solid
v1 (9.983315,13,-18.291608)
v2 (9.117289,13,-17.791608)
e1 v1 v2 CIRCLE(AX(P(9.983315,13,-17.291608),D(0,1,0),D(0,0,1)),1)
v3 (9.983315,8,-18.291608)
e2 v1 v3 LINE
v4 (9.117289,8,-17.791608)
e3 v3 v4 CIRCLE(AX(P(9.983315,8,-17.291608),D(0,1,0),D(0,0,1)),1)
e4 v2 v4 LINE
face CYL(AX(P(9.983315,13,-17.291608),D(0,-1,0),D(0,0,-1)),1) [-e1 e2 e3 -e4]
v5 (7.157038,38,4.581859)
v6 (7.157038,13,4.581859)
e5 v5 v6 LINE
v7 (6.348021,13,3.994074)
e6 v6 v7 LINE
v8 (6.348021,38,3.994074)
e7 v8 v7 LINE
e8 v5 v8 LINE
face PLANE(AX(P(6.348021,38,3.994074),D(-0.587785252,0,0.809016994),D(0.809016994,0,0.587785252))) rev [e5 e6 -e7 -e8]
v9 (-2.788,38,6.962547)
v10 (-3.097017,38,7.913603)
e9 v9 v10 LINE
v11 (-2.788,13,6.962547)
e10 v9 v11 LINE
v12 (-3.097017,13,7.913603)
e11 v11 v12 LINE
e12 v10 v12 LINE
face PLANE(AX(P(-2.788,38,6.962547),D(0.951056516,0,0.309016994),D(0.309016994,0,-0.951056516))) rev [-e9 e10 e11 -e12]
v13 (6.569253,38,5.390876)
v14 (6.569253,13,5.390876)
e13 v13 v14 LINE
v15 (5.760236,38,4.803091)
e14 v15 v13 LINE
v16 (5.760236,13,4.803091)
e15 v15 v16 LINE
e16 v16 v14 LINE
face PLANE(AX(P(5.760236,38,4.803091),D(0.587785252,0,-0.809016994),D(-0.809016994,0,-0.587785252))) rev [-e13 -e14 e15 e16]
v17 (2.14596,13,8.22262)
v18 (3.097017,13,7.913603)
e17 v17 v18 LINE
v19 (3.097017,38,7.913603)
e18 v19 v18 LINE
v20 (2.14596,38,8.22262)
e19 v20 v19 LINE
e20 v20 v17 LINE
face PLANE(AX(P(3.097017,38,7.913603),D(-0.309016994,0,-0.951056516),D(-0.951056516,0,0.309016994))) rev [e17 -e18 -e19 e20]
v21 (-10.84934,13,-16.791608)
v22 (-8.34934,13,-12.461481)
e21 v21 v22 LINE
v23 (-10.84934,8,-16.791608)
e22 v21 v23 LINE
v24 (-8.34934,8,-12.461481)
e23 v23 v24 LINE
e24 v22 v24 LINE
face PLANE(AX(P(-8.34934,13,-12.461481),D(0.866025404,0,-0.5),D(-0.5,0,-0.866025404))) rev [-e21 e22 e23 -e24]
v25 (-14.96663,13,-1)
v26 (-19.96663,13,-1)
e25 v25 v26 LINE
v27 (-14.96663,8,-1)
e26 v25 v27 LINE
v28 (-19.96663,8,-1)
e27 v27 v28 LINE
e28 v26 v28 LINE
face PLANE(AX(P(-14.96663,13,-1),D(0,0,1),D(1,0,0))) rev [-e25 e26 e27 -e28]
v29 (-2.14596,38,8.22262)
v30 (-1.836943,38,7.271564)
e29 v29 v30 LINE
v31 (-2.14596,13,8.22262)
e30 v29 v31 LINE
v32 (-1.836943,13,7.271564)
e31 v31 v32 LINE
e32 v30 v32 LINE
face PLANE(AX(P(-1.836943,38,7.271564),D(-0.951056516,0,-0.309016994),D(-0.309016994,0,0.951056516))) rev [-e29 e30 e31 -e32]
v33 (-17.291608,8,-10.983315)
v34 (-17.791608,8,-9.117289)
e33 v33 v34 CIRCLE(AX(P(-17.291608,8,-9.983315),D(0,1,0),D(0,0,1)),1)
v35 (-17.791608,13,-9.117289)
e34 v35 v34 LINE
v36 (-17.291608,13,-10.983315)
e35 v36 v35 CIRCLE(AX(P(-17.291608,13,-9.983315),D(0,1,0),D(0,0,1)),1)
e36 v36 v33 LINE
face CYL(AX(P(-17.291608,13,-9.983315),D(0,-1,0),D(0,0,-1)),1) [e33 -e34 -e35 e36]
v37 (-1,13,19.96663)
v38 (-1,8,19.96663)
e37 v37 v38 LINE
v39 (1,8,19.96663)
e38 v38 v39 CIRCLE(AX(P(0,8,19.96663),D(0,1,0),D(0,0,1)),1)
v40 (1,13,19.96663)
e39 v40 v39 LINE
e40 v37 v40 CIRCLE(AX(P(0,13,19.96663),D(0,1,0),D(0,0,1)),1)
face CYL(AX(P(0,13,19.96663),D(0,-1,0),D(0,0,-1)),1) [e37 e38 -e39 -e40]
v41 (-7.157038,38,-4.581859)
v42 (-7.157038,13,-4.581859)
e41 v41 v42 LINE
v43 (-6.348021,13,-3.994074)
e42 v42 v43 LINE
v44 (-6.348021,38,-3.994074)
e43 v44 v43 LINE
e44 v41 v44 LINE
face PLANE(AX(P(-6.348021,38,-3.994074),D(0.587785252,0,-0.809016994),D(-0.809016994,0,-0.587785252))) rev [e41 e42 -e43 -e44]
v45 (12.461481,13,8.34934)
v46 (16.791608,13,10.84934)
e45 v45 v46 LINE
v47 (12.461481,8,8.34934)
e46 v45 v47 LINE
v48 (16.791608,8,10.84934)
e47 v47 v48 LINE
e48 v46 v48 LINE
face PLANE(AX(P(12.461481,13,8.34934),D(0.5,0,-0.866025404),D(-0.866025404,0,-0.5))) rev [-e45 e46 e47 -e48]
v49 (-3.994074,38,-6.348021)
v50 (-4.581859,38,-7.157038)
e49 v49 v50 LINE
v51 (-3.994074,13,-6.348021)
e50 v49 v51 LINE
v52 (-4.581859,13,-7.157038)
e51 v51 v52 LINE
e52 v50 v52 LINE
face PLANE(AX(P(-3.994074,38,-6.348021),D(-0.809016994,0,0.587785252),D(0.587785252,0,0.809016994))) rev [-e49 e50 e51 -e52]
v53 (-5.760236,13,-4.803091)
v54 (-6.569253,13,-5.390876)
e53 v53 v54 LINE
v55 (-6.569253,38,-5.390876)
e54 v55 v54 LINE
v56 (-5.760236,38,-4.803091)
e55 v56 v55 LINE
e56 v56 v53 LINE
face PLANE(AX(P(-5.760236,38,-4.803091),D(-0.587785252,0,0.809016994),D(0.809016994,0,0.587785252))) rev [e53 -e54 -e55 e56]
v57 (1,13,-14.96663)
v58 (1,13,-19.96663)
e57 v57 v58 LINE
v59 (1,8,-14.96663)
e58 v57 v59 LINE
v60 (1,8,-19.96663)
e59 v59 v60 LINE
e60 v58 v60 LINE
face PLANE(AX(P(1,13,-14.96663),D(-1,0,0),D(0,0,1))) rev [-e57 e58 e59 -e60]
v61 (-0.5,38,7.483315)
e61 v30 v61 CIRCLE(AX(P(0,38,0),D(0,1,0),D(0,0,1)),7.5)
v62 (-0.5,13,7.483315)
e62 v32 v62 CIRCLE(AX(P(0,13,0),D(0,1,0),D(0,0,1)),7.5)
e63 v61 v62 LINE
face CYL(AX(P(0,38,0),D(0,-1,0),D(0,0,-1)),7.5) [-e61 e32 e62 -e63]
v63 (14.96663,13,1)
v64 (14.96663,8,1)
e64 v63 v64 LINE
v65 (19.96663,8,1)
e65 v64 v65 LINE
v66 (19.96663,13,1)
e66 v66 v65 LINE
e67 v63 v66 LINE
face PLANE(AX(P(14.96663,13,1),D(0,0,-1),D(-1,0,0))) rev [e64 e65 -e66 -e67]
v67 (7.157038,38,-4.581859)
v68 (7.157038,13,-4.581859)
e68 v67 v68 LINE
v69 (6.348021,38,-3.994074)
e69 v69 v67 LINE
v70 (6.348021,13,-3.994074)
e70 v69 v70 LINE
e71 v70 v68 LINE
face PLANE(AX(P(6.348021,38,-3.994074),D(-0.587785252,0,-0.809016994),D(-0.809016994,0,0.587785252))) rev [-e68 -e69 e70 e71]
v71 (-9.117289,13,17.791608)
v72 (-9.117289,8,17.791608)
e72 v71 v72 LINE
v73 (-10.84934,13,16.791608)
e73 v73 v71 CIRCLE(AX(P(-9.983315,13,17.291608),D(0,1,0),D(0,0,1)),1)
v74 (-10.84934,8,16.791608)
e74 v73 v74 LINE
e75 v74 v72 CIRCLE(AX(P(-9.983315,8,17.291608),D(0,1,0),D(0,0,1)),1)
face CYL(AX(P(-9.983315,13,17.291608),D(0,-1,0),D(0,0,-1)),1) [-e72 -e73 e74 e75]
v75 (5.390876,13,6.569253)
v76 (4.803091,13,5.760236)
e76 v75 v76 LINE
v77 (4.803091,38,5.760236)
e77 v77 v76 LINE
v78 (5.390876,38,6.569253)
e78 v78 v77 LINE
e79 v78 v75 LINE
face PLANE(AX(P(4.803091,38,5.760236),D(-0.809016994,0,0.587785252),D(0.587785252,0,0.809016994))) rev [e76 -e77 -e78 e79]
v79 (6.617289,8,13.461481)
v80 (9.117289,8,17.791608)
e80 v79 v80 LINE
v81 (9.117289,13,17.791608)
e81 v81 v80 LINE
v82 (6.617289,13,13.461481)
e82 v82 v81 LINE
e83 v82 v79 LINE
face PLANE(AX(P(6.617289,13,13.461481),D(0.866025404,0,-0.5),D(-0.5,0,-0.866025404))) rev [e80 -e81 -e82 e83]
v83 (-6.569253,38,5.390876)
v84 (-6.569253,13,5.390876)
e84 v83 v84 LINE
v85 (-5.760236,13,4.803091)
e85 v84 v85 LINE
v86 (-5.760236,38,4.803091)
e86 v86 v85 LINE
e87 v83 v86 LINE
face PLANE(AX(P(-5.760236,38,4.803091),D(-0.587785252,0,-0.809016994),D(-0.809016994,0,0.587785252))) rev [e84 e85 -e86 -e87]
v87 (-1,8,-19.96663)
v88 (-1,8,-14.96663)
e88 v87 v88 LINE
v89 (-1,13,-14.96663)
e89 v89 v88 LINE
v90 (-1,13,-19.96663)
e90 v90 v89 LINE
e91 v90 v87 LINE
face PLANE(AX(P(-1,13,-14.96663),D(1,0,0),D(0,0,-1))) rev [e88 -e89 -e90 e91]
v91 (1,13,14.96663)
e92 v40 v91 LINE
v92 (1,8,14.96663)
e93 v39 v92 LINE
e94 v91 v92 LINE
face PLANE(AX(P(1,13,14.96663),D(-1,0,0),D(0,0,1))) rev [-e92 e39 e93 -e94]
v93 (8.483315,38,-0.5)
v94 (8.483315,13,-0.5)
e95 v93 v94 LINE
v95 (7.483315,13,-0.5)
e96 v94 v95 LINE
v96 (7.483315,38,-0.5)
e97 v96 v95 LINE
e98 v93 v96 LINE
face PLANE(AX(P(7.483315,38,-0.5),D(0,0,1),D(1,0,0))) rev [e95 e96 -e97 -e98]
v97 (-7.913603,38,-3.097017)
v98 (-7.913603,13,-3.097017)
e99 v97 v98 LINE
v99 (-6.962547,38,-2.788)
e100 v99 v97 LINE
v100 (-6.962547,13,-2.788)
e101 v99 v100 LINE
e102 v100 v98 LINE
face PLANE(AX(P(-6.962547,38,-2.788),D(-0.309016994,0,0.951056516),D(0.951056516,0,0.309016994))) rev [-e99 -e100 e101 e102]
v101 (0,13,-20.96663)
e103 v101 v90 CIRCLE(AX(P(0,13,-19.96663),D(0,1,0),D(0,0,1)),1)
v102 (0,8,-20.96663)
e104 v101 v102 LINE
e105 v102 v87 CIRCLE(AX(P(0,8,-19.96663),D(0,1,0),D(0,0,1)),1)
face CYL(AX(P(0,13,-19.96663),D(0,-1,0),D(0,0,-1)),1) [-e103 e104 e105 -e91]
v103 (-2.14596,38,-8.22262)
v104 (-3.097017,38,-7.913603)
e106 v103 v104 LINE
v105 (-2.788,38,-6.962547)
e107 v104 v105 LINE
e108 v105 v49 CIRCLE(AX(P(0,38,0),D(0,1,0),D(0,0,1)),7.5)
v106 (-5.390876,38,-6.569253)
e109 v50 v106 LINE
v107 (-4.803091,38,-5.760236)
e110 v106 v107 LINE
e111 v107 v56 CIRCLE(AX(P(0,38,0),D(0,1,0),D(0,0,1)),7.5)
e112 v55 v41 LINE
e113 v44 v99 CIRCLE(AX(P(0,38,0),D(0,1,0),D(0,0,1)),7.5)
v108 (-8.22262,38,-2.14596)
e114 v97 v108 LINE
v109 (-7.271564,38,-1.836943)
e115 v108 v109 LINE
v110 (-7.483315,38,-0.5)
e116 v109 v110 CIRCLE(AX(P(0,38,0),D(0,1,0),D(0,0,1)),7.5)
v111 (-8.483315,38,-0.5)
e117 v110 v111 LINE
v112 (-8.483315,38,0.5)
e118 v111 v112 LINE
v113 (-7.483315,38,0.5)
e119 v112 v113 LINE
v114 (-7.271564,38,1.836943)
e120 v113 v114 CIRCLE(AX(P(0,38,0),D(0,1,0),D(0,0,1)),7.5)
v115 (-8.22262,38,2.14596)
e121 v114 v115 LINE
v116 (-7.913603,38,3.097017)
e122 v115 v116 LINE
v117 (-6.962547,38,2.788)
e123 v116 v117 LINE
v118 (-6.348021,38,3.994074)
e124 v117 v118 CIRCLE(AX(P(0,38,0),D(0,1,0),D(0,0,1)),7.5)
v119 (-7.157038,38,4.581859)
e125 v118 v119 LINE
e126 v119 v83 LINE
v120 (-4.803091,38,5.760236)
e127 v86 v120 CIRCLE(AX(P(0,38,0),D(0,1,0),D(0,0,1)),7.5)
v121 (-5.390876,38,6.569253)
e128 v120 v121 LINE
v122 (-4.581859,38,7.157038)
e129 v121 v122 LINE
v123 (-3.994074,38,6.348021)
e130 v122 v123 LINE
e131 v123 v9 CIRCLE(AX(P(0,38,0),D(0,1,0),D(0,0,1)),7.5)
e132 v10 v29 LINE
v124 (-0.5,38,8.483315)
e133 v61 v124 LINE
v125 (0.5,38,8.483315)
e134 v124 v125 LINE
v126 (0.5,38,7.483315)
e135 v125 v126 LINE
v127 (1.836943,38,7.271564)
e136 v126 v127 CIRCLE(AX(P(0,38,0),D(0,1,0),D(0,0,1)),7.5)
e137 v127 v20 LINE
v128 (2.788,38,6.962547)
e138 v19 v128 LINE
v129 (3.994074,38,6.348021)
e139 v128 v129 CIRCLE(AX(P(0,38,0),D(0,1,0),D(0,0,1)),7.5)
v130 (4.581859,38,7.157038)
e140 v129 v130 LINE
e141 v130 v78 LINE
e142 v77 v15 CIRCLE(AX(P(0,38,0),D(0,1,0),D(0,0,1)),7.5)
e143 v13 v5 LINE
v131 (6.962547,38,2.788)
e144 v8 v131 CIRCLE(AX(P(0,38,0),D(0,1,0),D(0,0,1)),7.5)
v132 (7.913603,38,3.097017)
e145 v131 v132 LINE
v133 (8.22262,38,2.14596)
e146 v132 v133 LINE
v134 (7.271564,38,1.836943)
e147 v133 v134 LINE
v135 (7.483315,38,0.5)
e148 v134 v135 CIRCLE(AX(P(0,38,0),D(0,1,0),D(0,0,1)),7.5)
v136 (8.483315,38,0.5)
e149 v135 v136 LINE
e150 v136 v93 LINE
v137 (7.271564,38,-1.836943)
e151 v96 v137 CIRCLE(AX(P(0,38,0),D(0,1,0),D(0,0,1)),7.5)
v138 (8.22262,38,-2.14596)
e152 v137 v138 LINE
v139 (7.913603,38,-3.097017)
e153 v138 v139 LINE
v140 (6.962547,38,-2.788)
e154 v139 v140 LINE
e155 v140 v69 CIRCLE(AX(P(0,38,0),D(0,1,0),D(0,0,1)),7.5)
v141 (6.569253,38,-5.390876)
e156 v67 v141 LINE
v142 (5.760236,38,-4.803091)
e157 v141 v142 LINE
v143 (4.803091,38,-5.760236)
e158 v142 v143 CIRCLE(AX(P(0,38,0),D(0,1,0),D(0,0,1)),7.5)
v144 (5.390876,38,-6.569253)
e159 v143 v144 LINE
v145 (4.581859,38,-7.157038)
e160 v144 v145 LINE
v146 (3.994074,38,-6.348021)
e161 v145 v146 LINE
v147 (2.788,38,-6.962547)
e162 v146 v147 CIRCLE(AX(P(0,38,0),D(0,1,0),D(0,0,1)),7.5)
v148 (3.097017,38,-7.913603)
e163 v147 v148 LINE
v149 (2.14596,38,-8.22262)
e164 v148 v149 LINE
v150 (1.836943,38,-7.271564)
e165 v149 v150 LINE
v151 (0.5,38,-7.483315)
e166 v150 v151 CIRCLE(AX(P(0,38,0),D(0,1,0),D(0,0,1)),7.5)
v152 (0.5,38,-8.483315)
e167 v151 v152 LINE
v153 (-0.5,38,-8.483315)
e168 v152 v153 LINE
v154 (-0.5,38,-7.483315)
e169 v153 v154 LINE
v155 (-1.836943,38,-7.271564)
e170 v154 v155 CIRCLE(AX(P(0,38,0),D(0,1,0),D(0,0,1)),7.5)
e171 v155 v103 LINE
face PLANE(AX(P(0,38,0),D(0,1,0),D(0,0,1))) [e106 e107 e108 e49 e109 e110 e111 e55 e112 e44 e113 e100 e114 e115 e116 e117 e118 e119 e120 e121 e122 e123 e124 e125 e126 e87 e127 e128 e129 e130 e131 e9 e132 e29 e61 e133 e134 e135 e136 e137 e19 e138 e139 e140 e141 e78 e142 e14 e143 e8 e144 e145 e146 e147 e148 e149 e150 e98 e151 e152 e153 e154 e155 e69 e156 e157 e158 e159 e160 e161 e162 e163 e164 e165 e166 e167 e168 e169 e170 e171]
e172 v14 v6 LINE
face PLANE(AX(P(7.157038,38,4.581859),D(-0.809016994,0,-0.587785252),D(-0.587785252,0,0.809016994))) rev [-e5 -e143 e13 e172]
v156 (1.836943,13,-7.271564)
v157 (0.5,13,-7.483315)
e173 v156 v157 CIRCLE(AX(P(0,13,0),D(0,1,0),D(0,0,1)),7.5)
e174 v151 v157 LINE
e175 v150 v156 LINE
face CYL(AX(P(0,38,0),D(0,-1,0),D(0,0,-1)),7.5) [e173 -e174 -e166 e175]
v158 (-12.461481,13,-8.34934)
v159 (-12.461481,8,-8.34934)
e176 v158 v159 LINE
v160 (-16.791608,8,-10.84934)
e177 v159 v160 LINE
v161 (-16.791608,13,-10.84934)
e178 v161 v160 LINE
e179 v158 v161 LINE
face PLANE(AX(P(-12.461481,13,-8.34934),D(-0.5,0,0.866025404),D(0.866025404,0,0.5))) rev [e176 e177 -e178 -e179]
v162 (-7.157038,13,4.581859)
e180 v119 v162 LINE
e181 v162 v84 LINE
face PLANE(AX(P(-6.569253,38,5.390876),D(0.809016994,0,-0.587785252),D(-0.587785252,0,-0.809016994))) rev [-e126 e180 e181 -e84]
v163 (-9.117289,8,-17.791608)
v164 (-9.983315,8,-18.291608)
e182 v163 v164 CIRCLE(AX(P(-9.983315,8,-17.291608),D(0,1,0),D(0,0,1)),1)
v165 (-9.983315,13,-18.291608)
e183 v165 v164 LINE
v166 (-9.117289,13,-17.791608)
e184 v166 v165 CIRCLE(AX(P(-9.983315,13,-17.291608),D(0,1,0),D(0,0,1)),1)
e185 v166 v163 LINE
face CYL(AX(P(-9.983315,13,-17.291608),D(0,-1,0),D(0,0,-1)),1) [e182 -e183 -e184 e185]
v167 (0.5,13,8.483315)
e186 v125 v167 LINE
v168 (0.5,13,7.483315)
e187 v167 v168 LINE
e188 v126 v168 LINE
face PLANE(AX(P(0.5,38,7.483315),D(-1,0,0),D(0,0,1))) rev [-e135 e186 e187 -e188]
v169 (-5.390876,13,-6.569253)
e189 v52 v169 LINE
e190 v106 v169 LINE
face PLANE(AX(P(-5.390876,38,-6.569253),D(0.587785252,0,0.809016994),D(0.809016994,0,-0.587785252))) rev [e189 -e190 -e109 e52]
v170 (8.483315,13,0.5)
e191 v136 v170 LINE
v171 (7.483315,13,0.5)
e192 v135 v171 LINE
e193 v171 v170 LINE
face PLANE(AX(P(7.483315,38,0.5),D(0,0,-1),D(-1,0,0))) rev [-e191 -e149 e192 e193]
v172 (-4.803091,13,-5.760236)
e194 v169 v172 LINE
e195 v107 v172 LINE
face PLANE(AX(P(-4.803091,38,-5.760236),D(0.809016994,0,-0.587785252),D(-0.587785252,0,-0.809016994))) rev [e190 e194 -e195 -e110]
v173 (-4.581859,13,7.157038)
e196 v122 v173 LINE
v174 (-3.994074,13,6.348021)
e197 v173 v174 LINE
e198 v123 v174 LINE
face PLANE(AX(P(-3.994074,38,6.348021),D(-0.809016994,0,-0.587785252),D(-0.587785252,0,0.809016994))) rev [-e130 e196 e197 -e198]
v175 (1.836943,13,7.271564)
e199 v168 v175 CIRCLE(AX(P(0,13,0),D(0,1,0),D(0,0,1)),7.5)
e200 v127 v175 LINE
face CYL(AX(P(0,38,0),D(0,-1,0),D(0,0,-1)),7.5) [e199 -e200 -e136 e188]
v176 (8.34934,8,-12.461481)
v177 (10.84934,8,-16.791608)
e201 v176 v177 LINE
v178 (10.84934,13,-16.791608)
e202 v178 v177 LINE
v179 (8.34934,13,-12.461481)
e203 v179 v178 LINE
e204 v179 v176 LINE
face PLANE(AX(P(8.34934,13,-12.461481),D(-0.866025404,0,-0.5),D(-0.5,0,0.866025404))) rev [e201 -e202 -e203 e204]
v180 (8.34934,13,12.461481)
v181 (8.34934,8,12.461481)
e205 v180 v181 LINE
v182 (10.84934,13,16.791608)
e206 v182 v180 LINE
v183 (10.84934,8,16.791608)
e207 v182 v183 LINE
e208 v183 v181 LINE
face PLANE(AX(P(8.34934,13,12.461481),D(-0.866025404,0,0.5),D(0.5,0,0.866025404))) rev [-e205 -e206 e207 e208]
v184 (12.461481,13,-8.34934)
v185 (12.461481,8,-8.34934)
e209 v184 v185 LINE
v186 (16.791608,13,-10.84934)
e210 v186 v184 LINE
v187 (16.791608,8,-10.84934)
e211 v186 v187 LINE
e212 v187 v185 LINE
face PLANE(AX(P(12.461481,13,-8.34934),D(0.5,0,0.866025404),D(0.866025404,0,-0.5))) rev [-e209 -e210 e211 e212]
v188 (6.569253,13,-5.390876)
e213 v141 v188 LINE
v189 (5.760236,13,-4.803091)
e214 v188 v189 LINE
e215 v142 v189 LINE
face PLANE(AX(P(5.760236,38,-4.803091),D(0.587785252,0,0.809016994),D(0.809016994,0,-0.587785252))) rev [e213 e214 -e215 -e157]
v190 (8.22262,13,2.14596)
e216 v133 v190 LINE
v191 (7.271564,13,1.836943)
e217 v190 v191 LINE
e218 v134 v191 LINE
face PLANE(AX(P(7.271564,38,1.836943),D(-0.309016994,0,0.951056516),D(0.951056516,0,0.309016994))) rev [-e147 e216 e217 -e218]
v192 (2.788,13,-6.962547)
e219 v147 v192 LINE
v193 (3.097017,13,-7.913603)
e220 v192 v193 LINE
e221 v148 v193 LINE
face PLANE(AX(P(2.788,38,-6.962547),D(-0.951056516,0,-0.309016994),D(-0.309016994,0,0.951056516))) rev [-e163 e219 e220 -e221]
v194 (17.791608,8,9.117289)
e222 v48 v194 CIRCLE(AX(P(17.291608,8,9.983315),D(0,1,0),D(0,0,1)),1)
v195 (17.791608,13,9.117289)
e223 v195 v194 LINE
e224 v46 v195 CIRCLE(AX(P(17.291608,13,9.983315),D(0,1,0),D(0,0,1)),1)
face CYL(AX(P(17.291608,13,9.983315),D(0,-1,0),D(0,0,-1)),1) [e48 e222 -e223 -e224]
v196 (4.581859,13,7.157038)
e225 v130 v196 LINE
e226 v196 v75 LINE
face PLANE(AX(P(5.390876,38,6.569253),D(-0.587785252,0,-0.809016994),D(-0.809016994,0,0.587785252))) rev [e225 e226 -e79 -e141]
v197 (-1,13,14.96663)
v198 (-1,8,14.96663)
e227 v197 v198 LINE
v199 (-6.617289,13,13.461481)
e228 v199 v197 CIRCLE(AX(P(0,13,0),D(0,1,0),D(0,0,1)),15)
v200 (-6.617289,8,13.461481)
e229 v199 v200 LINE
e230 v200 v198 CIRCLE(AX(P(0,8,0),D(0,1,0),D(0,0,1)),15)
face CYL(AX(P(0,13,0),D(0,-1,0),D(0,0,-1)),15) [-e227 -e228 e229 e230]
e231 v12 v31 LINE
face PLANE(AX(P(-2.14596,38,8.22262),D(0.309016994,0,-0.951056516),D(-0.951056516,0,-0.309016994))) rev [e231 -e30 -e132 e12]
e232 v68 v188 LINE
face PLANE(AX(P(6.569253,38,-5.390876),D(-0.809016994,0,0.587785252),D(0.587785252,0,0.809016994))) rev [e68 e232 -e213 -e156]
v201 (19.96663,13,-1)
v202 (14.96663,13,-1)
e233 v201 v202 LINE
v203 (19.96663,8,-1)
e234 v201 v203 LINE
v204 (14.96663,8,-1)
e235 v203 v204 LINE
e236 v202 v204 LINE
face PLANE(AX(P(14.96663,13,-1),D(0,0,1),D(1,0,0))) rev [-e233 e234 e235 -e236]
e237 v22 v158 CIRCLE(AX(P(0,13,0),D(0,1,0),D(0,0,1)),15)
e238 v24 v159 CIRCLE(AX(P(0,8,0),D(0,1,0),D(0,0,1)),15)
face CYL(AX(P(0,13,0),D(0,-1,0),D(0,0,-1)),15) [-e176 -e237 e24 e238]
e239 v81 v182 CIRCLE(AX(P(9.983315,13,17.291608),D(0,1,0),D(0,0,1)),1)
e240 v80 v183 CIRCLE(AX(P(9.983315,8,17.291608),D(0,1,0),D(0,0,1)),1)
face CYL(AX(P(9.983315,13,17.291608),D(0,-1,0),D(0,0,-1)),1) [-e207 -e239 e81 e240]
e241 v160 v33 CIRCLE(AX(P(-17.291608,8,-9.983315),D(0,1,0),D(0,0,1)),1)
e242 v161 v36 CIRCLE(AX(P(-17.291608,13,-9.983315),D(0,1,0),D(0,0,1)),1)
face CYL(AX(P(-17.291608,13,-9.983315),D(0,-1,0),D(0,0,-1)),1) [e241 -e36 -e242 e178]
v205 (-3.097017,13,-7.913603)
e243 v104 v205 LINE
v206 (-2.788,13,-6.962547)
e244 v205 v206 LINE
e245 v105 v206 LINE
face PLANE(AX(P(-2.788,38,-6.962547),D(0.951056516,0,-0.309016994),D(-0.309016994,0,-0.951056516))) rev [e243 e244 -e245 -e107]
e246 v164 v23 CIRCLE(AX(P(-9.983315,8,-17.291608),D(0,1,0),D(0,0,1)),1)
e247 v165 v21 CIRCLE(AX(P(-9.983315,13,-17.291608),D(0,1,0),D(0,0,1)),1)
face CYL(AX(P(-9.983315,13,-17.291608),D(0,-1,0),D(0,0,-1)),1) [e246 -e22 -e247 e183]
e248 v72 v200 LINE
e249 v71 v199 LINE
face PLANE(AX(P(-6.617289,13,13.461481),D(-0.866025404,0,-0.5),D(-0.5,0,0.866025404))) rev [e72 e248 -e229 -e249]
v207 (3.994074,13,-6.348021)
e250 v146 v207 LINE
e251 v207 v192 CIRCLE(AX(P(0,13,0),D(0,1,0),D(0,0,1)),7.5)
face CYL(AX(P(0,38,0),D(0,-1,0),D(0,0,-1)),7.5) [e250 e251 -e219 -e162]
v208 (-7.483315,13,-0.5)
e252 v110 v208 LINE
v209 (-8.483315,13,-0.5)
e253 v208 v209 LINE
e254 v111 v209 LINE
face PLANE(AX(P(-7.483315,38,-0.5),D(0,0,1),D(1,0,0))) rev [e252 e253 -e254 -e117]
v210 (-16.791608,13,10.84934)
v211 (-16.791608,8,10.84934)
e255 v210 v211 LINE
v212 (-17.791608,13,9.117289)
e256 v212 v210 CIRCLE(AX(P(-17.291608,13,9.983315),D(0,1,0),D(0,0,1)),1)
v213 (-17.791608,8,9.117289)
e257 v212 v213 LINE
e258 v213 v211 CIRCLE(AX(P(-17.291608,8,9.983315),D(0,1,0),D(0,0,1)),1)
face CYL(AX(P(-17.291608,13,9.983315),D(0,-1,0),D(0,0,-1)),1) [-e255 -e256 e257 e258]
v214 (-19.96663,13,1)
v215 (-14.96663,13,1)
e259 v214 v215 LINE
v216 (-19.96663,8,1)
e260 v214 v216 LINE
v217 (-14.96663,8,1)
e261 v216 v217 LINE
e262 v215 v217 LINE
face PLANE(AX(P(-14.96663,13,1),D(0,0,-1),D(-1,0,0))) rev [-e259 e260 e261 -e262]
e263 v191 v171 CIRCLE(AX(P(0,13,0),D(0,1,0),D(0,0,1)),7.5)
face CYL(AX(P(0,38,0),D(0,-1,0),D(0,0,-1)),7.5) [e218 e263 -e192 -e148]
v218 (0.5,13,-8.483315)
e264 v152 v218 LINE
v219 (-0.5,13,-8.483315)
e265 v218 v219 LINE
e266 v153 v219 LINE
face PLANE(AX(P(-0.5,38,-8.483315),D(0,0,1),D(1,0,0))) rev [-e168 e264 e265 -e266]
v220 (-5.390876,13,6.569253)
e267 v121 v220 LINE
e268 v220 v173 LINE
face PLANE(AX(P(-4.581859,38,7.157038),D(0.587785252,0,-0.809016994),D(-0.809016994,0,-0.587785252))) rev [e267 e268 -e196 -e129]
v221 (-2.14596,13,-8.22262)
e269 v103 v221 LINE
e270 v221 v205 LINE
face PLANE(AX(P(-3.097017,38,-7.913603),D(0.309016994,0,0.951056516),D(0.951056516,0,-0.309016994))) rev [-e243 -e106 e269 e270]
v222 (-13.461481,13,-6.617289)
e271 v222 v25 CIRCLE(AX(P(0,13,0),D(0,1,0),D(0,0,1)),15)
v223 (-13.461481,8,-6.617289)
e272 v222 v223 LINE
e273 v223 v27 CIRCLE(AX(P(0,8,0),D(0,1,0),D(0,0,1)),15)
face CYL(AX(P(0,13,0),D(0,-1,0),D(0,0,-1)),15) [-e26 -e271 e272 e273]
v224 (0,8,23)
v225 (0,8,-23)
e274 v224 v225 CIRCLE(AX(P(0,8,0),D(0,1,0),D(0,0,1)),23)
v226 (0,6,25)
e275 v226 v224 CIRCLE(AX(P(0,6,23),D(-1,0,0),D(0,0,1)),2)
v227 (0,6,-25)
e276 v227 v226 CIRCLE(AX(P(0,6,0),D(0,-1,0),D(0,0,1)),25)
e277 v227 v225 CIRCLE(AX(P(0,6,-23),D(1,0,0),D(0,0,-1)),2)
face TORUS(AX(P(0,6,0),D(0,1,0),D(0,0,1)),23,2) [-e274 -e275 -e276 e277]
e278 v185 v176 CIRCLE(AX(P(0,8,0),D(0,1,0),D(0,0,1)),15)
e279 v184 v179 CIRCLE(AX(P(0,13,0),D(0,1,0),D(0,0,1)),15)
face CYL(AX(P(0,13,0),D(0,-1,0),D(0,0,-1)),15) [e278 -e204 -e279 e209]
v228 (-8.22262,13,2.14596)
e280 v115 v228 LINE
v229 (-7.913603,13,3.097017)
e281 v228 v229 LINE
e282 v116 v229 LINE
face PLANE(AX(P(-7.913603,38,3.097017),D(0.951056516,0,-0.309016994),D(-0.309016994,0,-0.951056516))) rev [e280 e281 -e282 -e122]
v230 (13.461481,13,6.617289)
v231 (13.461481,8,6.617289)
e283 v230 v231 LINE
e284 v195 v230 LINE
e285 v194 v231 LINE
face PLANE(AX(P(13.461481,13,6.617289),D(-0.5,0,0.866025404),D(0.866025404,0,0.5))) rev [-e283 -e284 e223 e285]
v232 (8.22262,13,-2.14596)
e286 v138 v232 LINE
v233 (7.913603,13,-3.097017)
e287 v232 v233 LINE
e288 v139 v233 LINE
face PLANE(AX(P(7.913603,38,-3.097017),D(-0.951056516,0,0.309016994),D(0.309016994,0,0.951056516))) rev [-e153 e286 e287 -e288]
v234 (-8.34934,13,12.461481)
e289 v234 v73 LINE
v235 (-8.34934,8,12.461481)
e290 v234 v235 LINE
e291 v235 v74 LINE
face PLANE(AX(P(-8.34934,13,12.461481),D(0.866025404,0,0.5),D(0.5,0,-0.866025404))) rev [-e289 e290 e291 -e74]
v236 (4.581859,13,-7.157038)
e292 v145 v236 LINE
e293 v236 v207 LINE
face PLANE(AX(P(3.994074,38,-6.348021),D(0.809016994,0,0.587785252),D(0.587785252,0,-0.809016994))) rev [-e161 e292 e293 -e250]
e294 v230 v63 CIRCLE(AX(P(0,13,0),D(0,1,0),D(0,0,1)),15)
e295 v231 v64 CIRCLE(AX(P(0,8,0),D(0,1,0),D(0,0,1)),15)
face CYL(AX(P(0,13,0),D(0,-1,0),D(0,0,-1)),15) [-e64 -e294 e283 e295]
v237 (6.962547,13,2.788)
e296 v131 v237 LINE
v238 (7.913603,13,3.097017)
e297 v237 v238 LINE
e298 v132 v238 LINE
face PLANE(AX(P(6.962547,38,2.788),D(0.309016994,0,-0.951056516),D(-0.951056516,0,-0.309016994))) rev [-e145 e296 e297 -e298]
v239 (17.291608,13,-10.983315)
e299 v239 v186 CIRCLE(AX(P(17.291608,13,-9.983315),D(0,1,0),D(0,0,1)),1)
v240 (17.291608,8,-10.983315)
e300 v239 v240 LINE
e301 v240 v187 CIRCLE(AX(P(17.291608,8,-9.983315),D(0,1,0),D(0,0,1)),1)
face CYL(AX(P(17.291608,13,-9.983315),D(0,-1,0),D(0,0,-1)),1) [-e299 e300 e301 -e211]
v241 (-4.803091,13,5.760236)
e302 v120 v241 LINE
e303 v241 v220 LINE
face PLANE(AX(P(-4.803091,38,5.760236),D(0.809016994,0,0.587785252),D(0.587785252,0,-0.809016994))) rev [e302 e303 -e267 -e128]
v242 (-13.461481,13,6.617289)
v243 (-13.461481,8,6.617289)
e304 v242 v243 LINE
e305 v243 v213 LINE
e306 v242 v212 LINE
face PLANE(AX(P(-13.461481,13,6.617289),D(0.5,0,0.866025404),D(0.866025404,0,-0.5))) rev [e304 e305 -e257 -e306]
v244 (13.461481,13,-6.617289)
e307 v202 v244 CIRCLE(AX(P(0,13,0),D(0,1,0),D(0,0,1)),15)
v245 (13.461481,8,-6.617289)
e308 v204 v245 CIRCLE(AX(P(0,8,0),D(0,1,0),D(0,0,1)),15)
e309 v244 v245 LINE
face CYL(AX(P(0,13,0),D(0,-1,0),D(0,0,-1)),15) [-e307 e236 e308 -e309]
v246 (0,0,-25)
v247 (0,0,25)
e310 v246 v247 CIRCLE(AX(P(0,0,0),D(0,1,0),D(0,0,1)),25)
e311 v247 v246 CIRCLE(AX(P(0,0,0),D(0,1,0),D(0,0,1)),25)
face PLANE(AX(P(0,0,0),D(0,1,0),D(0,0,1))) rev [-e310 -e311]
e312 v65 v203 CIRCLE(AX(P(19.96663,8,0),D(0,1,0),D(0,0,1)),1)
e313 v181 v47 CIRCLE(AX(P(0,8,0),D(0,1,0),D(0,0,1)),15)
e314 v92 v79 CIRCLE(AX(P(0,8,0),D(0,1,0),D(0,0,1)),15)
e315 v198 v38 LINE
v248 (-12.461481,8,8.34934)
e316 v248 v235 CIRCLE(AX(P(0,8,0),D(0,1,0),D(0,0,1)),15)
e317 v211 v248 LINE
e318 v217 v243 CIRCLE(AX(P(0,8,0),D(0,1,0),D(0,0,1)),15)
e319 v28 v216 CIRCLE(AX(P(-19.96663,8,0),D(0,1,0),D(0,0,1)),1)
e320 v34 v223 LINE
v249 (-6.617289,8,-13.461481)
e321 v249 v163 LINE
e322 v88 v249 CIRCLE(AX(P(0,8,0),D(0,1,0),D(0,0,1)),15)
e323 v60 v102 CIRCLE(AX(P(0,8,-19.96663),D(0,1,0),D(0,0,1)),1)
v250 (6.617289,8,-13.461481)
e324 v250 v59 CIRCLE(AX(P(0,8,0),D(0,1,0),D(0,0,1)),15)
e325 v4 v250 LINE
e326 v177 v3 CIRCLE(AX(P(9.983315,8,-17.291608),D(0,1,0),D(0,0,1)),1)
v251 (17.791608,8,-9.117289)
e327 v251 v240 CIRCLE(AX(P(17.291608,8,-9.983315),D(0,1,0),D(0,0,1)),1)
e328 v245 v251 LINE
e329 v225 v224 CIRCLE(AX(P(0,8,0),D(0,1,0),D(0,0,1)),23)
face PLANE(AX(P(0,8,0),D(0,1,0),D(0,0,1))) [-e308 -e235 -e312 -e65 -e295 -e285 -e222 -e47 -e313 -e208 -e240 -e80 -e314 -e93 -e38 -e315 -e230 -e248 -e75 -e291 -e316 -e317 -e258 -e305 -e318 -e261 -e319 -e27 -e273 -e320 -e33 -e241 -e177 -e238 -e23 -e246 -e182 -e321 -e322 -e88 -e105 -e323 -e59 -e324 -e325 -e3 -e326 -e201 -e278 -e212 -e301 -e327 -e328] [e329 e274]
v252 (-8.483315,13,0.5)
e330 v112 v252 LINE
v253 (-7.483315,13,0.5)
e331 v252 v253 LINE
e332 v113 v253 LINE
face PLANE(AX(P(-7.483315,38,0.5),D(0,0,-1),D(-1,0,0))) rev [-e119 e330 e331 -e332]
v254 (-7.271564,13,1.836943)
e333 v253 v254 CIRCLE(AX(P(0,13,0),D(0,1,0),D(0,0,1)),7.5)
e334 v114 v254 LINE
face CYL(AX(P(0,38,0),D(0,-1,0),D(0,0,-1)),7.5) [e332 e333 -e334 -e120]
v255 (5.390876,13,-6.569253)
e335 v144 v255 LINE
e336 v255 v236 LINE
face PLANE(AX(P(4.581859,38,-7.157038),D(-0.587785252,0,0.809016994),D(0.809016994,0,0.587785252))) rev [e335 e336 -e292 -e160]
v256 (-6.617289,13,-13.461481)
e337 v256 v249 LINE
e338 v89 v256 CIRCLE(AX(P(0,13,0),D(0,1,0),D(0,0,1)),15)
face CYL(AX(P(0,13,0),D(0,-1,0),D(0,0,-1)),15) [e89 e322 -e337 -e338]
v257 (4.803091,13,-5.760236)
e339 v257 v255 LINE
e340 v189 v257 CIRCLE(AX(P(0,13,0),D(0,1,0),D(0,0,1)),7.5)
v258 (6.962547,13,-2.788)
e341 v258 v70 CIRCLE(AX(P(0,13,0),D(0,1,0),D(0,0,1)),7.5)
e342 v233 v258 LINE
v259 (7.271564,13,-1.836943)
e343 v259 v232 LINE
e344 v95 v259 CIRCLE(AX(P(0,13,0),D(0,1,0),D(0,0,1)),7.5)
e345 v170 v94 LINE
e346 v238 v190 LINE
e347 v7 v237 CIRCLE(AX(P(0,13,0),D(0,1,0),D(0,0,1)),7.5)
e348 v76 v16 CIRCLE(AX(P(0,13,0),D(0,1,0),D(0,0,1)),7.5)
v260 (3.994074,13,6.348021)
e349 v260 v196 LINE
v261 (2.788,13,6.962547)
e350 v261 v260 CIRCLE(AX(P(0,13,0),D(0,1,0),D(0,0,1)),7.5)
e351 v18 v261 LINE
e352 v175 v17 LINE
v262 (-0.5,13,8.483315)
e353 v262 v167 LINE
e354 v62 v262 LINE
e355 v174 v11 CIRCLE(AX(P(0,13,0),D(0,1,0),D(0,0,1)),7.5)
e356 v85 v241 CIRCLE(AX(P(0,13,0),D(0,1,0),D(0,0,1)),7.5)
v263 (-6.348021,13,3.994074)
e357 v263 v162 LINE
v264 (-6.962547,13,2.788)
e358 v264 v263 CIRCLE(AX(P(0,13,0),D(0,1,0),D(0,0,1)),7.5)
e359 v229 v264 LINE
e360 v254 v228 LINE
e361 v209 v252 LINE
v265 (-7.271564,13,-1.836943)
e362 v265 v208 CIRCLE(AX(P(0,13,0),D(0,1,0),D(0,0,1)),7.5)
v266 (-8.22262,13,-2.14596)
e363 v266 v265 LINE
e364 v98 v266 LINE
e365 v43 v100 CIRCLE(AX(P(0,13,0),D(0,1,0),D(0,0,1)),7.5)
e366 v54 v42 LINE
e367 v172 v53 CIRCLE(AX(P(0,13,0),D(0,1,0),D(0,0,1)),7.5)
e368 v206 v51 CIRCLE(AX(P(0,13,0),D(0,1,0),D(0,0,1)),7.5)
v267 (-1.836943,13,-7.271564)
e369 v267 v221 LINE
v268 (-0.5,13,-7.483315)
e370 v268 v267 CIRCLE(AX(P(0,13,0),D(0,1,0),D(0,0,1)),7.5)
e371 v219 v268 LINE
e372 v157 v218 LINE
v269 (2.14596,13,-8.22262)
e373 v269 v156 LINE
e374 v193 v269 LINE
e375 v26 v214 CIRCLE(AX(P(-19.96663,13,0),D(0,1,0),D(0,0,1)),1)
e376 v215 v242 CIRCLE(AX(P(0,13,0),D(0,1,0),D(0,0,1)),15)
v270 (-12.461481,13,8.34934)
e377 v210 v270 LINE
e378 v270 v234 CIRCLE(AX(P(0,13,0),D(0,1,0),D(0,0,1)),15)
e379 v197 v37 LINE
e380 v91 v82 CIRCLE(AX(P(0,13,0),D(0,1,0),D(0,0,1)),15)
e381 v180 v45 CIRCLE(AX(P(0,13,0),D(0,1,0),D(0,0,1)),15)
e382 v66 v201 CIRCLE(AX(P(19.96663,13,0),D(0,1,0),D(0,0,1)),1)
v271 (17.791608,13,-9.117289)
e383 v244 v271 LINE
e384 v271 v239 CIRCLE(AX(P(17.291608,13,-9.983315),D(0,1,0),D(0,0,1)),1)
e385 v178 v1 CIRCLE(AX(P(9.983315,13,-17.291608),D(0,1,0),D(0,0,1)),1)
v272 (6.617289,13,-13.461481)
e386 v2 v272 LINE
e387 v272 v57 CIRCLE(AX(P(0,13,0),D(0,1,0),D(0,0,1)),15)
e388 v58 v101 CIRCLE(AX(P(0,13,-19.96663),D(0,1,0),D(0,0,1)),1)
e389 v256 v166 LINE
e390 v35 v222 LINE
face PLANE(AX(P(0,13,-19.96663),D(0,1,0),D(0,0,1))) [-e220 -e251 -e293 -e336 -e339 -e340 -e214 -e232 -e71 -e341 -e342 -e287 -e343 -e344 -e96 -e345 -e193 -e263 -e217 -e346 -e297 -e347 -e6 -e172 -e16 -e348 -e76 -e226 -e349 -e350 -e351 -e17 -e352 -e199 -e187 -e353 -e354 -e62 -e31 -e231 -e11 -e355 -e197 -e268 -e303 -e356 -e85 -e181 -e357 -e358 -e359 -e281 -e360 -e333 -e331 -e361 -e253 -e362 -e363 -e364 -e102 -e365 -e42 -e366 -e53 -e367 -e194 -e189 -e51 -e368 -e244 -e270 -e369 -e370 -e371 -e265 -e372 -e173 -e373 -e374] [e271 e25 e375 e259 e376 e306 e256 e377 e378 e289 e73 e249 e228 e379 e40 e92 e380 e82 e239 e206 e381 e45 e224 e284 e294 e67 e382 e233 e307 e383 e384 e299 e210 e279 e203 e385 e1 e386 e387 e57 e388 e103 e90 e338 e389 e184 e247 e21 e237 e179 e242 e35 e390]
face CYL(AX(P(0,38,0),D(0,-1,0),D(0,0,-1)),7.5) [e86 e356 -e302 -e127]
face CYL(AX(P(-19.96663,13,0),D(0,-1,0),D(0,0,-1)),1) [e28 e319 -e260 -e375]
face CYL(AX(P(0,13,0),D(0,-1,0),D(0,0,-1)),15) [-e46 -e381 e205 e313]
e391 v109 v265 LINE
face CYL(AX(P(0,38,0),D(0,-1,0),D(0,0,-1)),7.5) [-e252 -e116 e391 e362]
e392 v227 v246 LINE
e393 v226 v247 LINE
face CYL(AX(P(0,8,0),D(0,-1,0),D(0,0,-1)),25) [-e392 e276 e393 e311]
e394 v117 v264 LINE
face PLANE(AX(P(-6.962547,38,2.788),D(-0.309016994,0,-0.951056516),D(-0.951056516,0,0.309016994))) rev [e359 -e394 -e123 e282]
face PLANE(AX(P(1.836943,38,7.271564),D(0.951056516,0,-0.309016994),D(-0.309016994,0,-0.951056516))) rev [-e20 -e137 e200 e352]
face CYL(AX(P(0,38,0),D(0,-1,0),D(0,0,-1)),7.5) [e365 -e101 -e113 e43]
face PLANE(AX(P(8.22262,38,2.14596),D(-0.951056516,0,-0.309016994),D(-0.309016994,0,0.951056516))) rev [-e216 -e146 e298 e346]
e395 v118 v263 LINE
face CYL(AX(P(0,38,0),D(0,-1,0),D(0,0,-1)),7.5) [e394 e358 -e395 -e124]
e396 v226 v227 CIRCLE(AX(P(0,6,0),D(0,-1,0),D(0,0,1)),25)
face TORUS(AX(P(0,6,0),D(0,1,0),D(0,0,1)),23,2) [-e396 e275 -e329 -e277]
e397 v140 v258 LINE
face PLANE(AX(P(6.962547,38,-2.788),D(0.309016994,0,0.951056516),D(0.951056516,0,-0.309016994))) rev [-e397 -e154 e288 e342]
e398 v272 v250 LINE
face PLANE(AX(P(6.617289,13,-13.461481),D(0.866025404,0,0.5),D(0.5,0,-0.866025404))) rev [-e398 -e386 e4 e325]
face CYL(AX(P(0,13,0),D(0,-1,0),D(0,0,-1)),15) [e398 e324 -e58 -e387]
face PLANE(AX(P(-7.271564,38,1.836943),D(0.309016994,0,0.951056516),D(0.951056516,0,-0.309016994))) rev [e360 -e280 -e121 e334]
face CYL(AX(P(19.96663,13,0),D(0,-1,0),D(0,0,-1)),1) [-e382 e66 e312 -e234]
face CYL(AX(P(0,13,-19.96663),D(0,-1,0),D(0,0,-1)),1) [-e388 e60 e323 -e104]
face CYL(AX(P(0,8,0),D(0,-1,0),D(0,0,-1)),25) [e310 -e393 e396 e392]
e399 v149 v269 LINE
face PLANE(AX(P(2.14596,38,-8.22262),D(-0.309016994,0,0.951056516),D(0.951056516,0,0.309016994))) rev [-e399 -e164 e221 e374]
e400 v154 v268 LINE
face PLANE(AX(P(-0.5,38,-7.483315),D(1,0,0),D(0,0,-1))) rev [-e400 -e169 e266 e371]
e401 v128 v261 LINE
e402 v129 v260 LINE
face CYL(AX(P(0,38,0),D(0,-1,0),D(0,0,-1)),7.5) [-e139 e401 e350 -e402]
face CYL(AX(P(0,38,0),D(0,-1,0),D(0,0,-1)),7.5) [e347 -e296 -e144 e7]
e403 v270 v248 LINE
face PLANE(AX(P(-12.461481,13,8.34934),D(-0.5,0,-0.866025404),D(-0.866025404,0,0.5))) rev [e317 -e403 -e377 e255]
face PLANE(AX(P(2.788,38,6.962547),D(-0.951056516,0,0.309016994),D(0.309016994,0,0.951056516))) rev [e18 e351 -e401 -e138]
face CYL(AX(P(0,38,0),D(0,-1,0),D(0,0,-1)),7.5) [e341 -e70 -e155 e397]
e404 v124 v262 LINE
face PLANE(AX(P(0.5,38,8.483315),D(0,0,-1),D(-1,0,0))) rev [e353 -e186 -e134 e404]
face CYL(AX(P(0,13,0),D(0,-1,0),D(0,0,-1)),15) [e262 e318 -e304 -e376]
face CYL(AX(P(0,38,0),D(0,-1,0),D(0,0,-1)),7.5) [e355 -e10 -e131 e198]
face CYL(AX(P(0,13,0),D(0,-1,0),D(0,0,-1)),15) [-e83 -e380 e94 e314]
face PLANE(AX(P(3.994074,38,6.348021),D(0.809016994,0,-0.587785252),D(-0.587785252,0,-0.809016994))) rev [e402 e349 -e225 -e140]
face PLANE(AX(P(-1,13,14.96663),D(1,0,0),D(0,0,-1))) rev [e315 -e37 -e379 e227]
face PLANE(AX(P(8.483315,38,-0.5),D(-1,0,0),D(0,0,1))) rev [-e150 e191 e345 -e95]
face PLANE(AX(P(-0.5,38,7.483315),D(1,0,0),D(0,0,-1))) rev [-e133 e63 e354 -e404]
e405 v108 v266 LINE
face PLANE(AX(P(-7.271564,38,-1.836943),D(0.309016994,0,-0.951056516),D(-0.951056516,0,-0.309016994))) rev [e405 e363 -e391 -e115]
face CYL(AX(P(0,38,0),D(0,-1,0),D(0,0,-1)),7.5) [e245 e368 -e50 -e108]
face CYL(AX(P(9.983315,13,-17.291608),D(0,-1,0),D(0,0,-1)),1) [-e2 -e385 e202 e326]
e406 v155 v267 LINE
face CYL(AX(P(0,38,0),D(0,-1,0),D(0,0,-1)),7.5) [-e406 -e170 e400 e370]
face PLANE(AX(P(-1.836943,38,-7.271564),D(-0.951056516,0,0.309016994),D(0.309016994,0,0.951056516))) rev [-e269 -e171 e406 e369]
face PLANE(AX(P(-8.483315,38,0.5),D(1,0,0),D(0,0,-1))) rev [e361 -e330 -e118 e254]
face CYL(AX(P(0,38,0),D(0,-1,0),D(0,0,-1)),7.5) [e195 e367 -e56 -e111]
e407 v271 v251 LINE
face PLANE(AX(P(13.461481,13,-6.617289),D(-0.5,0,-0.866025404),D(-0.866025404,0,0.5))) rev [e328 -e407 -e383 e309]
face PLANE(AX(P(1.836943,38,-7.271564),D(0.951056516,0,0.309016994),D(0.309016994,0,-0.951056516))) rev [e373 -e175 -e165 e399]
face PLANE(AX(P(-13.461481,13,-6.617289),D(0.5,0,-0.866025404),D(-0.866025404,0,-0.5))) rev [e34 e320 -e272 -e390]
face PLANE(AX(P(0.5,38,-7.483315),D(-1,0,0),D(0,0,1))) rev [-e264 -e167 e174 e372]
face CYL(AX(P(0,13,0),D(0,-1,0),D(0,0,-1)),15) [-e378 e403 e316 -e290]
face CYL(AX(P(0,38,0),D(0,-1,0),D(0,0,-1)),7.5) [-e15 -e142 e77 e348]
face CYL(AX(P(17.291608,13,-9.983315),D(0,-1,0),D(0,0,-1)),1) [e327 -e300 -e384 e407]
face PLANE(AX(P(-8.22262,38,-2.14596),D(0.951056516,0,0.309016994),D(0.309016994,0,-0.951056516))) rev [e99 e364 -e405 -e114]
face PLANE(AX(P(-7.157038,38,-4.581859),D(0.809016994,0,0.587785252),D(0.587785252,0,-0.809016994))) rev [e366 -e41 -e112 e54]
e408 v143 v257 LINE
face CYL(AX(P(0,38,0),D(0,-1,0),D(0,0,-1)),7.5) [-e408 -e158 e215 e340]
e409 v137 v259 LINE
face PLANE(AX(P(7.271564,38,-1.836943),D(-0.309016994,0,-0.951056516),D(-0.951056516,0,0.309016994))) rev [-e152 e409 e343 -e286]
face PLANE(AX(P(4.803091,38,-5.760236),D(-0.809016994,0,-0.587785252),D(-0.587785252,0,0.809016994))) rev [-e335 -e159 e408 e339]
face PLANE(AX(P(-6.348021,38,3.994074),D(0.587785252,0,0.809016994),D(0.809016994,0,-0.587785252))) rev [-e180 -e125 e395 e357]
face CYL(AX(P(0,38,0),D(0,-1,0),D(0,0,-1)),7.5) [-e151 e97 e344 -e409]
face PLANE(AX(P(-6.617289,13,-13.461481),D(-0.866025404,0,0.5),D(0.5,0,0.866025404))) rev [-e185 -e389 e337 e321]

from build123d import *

# Parameters (mm, degrees)
BASE_DISC_SKETCH_R        = 25
BASE_DISC_50_DEPTH        = 8
TOOTH_RING_12T_30_DEPTH   = 5
SPLINE_SHAFT_20T_15_DEPTH = 25
BASE_EDGE_FILLET_R2_R     = 2


with BuildPart() as part:
    # Base Disc Sketch → Base Disc Ø50 (new body)
    with BuildSketch(Plane(origin=(0, 0, 0), x_dir=(1, 0, 0), z_dir=(0, 1, 0))):
        with Locations(Location((0, 0, 0), (0, 0, 270))):
            Circle(BASE_DISC_SKETCH_R)
    extrude(amount=BASE_DISC_50_DEPTH)

    # Tooth Ring Sketch → Tooth Ring 12T Ø30 (add)
    with BuildSketch(Plane(origin=(0, 8, 0), x_dir=(1, 0, 0), z_dir=(0, 1, 0))):
        with BuildLine():
            Line((8.349340177, 12.461481397), (10.849340177, 16.791608416))
            ThreePointArc((10.849340177, 16.791608416), (10.483314774, 18.15763382), (9.11728937, 17.791608416))
            Line((9.11728937, 17.791608416), (6.61728937, 13.461481397))
            ThreePointArc((6.61728937, 13.461481397), (3.882285677, 14.488887394), (1, 14.966629547))
            Line((1, 14.966629547), (1, 19.966629547))
            ThreePointArc((1, 19.966629547), (0, 20.966629547), (-1, 19.966629547))
            Line((-1, 19.966629547), (-1, 14.966629547))
            ThreePointArc((-1, 14.966629547), (-3.882285677, 14.488887394), (-6.61728937, 13.461481397))
            Line((-6.61728937, 13.461481397), (-9.11728937, 17.791608416))
            ThreePointArc((-9.11728937, 17.791608416), (-10.483314774, 18.15763382), (-10.849340177, 16.791608416))
            Line((-10.849340177, 16.791608416), (-8.349340177, 12.461481397))
            ThreePointArc((-8.349340177, 12.461481397), (-10.606601718, 10.606601718), (-12.461481397, 8.349340177))
            Line((-12.461481397, 8.349340177), (-16.791608416, 10.849340177))
            ThreePointArc((-16.791608416, 10.849340177), (-18.15763382, 10.483314774), (-17.791608416, 9.11728937))
            Line((-17.791608416, 9.11728937), (-13.461481397, 6.61728937))
            ThreePointArc((-13.461481397, 6.61728937), (-14.488887394, 3.882285677), (-14.966629547, 1))
            Line((-14.966629547, 1), (-19.966629547, 1))
            ThreePointArc((-19.966629547, 1), (-20.966629547, 0), (-19.966629547, -1))
            Line((-19.966629547, -1), (-14.966629547, -1))
            ThreePointArc((-14.966629547, -1), (-14.488887394, -3.882285677), (-13.461481397, -6.61728937))
            Line((-13.461481397, -6.61728937), (-17.791608416, -9.11728937))
            ThreePointArc((-17.791608416, -9.11728937), (-18.15763382, -10.483314774), (-16.791608416, -10.849340177))
            Line((-16.791608416, -10.849340177), (-12.461481397, -8.349340177))
            ThreePointArc((-12.461481397, -8.349340177), (-10.606601718, -10.606601718), (-8.349340177, -12.461481397))
            Line((-8.349340177, -12.461481397), (-10.849340177, -16.791608416))
            ThreePointArc((-10.849340177, -16.791608416), (-10.483314774, -18.15763382), (-9.11728937, -17.791608416))
            Line((-9.11728937, -17.791608416), (-6.61728937, -13.461481397))
            ThreePointArc((-6.61728937, -13.461481397), (-3.882285677, -14.488887394), (-1, -14.966629547))
            Line((-1, -14.966629547), (-1, -19.966629547))
            ThreePointArc((-1, -19.966629547), (0, -20.966629547), (1, -19.966629547))
            Line((1, -19.966629547), (1, -14.966629547))
            ThreePointArc((1, -14.966629547), (3.882285677, -14.488887394), (6.61728937, -13.461481397))
            Line((6.61728937, -13.461481397), (9.11728937, -17.791608416))
            ThreePointArc((9.11728937, -17.791608416), (10.483314774, -18.15763382), (10.849340177, -16.791608416))
            Line((10.849340177, -16.791608416), (8.349340177, -12.461481397))
            ThreePointArc((8.349340177, -12.461481397), (10.606601718, -10.606601718), (12.461481397, -8.349340177))
            Line((12.461481397, -8.349340177), (16.791608416, -10.849340177))
            ThreePointArc((16.791608416, -10.849340177), (18.15763382, -10.483314774), (17.791608416, -9.11728937))
            Line((17.791608416, -9.11728937), (13.461481397, -6.61728937))
            ThreePointArc((13.461481397, -6.61728937), (14.488887394, -3.882285677), (14.966629547, -1))
            Line((14.966629547, -1), (19.966629547, -1))
            ThreePointArc((19.966629547, -1), (20.966629547, 0), (19.966629547, 1))
            Line((19.966629547, 1), (14.966629547, 1))
            ThreePointArc((14.966629547, 1), (14.488887394, 3.882285677), (13.461481397, 6.61728937))
            Line((13.461481397, 6.61728937), (17.791608416, 9.11728937))
            ThreePointArc((17.791608416, 9.11728937), (18.15763382, 10.483314774), (16.791608416, 10.849340177))
            Line((16.791608416, 10.849340177), (12.461481397, 8.349340177))
            ThreePointArc((12.461481397, 8.349340177), (10.606601718, 10.606601718), (8.349340177, 12.461481397))
        make_face()
    extrude(amount=TOOTH_RING_12T_30_DEPTH)

    # Spline Shaft Sketch → Spline Shaft 20T Ø15 (add)
    with BuildSketch(Plane(origin=(0, 13, 0), x_dir=(1, 0, 0), z_dir=(0, 1, 0))):
        with BuildLine():
            Line((1.836943181, 7.271563776), (2.145960176, 8.222620292))
            Line((2.145960176, 8.222620292), (3.097016692, 7.913603298))
            Line((3.097016692, 7.913603298), (2.787999697, 6.962546782))
            ThreePointArc((2.787999697, 6.962546782), (3.404928748, 6.682548931), (3.994073565, 6.348021452))
            Line((3.994073565, 6.348021452), (4.581858817, 7.157038447))
            Line((4.581858817, 7.157038447), (5.390875812, 6.569253194))
            Line((5.390875812, 6.569253194), (4.803090559, 5.7602362))
            ThreePointArc((4.803090559, 5.7602362), (5.303300859, 5.303300859), (5.7602362, 4.803090559))
            Line((5.7602362, 4.803090559), (6.569253194, 5.390875812))
            Line((6.569253194, 5.390875812), (7.157038447, 4.581858817))
            Line((7.157038447, 4.581858817), (6.348021452, 3.994073565))
            ThreePointArc((6.348021452, 3.994073565), (6.682548931, 3.404928748), (6.962546782, 2.787999697))
            Line((6.962546782, 2.787999697), (7.913603298, 3.097016692))
            Line((7.913603298, 3.097016692), (8.222620292, 2.145960176))
            Line((8.222620292, 2.145960176), (7.271563776, 1.836943181))
            ThreePointArc((7.271563776, 1.836943181), (7.407662554, 1.173258488), (7.483314774, 0.5))
            Line((7.483314774, 0.5), (8.483314774, 0.5))
            Line((8.483314774, 0.5), (8.483314774, -0.5))
            Line((8.483314774, -0.5), (7.483314774, -0.5))
            ThreePointArc((7.483314774, -0.5), (7.407662554, -1.173258488), (7.271563776, -1.836943181))
            Line((7.271563776, -1.836943181), (8.222620292, -2.145960176))
            Line((8.222620292, -2.145960176), (7.913603298, -3.097016692))
            Line((7.913603298, -3.097016692), (6.962546782, -2.787999697))
            ThreePointArc((6.962546782, -2.787999697), (6.682548931, -3.404928748), (6.348021452, -3.994073565))
            Line((6.348021452, -3.994073565), (7.157038447, -4.581858817))
            Line((7.157038447, -4.581858817), (6.569253194, -5.390875812))
            Line((6.569253194, -5.390875812), (5.7602362, -4.803090559))
            ThreePointArc((5.7602362, -4.803090559), (5.303300859, -5.303300859), (4.803090559, -5.7602362))
            Line((4.803090559, -5.7602362), (5.390875812, -6.569253194))
            Line((5.390875812, -6.569253194), (4.581858817, -7.157038447))
            Line((4.581858817, -7.157038447), (3.994073565, -6.348021452))
            ThreePointArc((3.994073565, -6.348021452), (3.404928748, -6.682548931), (2.787999697, -6.962546782))
            Line((2.787999697, -6.962546782), (3.097016692, -7.913603298))
            Line((3.097016692, -7.913603298), (2.145960176, -8.222620292))
            Line((2.145960176, -8.222620292), (1.836943181, -7.271563776))
            ThreePointArc((1.836943181, -7.271563776), (1.173258488, -7.407662554), (0.5, -7.483314774))
            Line((0.5, -7.483314774), (0.5, -8.483314774))
            Line((0.5, -8.483314774), (-0.5, -8.483314774))
            Line((-0.5, -8.483314774), (-0.5, -7.483314774))
            ThreePointArc((-0.5, -7.483314774), (-1.173258488, -7.407662554), (-1.836943181, -7.271563776))
            Line((-1.836943181, -7.271563776), (-2.145960176, -8.222620292))
            Line((-2.145960176, -8.222620292), (-3.097016692, -7.913603298))
            Line((-3.097016692, -7.913603298), (-2.787999697, -6.962546782))
            ThreePointArc((-2.787999697, -6.962546782), (-3.404928748, -6.682548931), (-3.994073565, -6.348021452))
            Line((-3.994073565, -6.348021452), (-4.581858817, -7.157038447))
            Line((-4.581858817, -7.157038447), (-5.390875812, -6.569253194))
            Line((-5.390875812, -6.569253194), (-4.803090559, -5.7602362))
            ThreePointArc((-4.803090559, -5.7602362), (-5.303300859, -5.303300859), (-5.7602362, -4.803090559))
            Line((-5.7602362, -4.803090559), (-6.569253194, -5.390875812))
            Line((-6.569253194, -5.390875812), (-7.157038447, -4.581858817))
            Line((-7.157038447, -4.581858817), (-6.348021452, -3.994073565))
            ThreePointArc((-6.348021452, -3.994073565), (-6.682548931, -3.404928748), (-6.962546782, -2.787999697))
            Line((-6.962546782, -2.787999697), (-7.913603298, -3.097016692))
            Line((-7.913603298, -3.097016692), (-8.222620292, -2.145960176))
            Line((-8.222620292, -2.145960176), (-7.271563776, -1.836943181))
            ThreePointArc((-7.271563776, -1.836943181), (-7.407662554, -1.173258488), (-7.483314774, -0.5))
            Line((-7.483314774, -0.5), (-8.483314774, -0.5))
            Line((-8.483314774, -0.5), (-8.483314774, 0.5))
            Line((-8.483314774, 0.5), (-7.483314774, 0.5))
            ThreePointArc((-7.483314774, 0.5), (-7.407662554, 1.173258488), (-7.271563776, 1.836943181))
            Line((-7.271563776, 1.836943181), (-8.222620292, 2.145960176))
            Line((-8.222620292, 2.145960176), (-7.913603298, 3.097016692))
            Line((-7.913603298, 3.097016692), (-6.962546782, 2.787999697))
            ThreePointArc((-6.962546782, 2.787999697), (-6.682548931, 3.404928748), (-6.348021452, 3.994073565))
            Line((-6.348021452, 3.994073565), (-7.157038447, 4.581858817))
            Line((-7.157038447, 4.581858817), (-6.569253194, 5.390875812))
            Line((-6.569253194, 5.390875812), (-5.7602362, 4.803090559))
            ThreePointArc((-5.7602362, 4.803090559), (-5.303300859, 5.303300859), (-4.803090559, 5.7602362))
            Line((-4.803090559, 5.7602362), (-5.390875812, 6.569253194))
            Line((-5.390875812, 6.569253194), (-4.581858817, 7.157038447))
            Line((-4.581858817, 7.157038447), (-3.994073565, 6.348021452))
            ThreePointArc((-3.994073565, 6.348021452), (-3.404928748, 6.682548931), (-2.787999697, 6.962546782))
            Line((-2.787999697, 6.962546782), (-3.097016692, 7.913603298))
            Line((-3.097016692, 7.913603298), (-2.145960176, 8.222620292))
            Line((-2.145960176, 8.222620292), (-1.836943181, 7.271563776))
            ThreePointArc((-1.836943181, 7.271563776), (-1.173258488, 7.407662554), (-0.5, 7.483314774))
            Line((-0.5, 7.483314774), (-0.5, 8.483314774))
            Line((-0.5, 8.483314774), (0.5, 8.483314774))
            Line((0.5, 8.483314774), (0.5, 7.483314774))
            ThreePointArc((0.5, 7.483314774), (1.173258488, 7.407662554), (1.836943181, 7.271563776))
        make_face()
    extrude(amount=SPLINE_SHAFT_20T_15_DEPTH)

    # Base Edge Fillet R2
    base_edge_fillet_r2_edges = [part.edges().sort_by_distance(p)[0] for p in [
        (0, 8, -25),
    ]]
    fillet(base_edge_fillet_r2_edges, radius=BASE_EDGE_FILLET_R2_R)


solid = part.part
